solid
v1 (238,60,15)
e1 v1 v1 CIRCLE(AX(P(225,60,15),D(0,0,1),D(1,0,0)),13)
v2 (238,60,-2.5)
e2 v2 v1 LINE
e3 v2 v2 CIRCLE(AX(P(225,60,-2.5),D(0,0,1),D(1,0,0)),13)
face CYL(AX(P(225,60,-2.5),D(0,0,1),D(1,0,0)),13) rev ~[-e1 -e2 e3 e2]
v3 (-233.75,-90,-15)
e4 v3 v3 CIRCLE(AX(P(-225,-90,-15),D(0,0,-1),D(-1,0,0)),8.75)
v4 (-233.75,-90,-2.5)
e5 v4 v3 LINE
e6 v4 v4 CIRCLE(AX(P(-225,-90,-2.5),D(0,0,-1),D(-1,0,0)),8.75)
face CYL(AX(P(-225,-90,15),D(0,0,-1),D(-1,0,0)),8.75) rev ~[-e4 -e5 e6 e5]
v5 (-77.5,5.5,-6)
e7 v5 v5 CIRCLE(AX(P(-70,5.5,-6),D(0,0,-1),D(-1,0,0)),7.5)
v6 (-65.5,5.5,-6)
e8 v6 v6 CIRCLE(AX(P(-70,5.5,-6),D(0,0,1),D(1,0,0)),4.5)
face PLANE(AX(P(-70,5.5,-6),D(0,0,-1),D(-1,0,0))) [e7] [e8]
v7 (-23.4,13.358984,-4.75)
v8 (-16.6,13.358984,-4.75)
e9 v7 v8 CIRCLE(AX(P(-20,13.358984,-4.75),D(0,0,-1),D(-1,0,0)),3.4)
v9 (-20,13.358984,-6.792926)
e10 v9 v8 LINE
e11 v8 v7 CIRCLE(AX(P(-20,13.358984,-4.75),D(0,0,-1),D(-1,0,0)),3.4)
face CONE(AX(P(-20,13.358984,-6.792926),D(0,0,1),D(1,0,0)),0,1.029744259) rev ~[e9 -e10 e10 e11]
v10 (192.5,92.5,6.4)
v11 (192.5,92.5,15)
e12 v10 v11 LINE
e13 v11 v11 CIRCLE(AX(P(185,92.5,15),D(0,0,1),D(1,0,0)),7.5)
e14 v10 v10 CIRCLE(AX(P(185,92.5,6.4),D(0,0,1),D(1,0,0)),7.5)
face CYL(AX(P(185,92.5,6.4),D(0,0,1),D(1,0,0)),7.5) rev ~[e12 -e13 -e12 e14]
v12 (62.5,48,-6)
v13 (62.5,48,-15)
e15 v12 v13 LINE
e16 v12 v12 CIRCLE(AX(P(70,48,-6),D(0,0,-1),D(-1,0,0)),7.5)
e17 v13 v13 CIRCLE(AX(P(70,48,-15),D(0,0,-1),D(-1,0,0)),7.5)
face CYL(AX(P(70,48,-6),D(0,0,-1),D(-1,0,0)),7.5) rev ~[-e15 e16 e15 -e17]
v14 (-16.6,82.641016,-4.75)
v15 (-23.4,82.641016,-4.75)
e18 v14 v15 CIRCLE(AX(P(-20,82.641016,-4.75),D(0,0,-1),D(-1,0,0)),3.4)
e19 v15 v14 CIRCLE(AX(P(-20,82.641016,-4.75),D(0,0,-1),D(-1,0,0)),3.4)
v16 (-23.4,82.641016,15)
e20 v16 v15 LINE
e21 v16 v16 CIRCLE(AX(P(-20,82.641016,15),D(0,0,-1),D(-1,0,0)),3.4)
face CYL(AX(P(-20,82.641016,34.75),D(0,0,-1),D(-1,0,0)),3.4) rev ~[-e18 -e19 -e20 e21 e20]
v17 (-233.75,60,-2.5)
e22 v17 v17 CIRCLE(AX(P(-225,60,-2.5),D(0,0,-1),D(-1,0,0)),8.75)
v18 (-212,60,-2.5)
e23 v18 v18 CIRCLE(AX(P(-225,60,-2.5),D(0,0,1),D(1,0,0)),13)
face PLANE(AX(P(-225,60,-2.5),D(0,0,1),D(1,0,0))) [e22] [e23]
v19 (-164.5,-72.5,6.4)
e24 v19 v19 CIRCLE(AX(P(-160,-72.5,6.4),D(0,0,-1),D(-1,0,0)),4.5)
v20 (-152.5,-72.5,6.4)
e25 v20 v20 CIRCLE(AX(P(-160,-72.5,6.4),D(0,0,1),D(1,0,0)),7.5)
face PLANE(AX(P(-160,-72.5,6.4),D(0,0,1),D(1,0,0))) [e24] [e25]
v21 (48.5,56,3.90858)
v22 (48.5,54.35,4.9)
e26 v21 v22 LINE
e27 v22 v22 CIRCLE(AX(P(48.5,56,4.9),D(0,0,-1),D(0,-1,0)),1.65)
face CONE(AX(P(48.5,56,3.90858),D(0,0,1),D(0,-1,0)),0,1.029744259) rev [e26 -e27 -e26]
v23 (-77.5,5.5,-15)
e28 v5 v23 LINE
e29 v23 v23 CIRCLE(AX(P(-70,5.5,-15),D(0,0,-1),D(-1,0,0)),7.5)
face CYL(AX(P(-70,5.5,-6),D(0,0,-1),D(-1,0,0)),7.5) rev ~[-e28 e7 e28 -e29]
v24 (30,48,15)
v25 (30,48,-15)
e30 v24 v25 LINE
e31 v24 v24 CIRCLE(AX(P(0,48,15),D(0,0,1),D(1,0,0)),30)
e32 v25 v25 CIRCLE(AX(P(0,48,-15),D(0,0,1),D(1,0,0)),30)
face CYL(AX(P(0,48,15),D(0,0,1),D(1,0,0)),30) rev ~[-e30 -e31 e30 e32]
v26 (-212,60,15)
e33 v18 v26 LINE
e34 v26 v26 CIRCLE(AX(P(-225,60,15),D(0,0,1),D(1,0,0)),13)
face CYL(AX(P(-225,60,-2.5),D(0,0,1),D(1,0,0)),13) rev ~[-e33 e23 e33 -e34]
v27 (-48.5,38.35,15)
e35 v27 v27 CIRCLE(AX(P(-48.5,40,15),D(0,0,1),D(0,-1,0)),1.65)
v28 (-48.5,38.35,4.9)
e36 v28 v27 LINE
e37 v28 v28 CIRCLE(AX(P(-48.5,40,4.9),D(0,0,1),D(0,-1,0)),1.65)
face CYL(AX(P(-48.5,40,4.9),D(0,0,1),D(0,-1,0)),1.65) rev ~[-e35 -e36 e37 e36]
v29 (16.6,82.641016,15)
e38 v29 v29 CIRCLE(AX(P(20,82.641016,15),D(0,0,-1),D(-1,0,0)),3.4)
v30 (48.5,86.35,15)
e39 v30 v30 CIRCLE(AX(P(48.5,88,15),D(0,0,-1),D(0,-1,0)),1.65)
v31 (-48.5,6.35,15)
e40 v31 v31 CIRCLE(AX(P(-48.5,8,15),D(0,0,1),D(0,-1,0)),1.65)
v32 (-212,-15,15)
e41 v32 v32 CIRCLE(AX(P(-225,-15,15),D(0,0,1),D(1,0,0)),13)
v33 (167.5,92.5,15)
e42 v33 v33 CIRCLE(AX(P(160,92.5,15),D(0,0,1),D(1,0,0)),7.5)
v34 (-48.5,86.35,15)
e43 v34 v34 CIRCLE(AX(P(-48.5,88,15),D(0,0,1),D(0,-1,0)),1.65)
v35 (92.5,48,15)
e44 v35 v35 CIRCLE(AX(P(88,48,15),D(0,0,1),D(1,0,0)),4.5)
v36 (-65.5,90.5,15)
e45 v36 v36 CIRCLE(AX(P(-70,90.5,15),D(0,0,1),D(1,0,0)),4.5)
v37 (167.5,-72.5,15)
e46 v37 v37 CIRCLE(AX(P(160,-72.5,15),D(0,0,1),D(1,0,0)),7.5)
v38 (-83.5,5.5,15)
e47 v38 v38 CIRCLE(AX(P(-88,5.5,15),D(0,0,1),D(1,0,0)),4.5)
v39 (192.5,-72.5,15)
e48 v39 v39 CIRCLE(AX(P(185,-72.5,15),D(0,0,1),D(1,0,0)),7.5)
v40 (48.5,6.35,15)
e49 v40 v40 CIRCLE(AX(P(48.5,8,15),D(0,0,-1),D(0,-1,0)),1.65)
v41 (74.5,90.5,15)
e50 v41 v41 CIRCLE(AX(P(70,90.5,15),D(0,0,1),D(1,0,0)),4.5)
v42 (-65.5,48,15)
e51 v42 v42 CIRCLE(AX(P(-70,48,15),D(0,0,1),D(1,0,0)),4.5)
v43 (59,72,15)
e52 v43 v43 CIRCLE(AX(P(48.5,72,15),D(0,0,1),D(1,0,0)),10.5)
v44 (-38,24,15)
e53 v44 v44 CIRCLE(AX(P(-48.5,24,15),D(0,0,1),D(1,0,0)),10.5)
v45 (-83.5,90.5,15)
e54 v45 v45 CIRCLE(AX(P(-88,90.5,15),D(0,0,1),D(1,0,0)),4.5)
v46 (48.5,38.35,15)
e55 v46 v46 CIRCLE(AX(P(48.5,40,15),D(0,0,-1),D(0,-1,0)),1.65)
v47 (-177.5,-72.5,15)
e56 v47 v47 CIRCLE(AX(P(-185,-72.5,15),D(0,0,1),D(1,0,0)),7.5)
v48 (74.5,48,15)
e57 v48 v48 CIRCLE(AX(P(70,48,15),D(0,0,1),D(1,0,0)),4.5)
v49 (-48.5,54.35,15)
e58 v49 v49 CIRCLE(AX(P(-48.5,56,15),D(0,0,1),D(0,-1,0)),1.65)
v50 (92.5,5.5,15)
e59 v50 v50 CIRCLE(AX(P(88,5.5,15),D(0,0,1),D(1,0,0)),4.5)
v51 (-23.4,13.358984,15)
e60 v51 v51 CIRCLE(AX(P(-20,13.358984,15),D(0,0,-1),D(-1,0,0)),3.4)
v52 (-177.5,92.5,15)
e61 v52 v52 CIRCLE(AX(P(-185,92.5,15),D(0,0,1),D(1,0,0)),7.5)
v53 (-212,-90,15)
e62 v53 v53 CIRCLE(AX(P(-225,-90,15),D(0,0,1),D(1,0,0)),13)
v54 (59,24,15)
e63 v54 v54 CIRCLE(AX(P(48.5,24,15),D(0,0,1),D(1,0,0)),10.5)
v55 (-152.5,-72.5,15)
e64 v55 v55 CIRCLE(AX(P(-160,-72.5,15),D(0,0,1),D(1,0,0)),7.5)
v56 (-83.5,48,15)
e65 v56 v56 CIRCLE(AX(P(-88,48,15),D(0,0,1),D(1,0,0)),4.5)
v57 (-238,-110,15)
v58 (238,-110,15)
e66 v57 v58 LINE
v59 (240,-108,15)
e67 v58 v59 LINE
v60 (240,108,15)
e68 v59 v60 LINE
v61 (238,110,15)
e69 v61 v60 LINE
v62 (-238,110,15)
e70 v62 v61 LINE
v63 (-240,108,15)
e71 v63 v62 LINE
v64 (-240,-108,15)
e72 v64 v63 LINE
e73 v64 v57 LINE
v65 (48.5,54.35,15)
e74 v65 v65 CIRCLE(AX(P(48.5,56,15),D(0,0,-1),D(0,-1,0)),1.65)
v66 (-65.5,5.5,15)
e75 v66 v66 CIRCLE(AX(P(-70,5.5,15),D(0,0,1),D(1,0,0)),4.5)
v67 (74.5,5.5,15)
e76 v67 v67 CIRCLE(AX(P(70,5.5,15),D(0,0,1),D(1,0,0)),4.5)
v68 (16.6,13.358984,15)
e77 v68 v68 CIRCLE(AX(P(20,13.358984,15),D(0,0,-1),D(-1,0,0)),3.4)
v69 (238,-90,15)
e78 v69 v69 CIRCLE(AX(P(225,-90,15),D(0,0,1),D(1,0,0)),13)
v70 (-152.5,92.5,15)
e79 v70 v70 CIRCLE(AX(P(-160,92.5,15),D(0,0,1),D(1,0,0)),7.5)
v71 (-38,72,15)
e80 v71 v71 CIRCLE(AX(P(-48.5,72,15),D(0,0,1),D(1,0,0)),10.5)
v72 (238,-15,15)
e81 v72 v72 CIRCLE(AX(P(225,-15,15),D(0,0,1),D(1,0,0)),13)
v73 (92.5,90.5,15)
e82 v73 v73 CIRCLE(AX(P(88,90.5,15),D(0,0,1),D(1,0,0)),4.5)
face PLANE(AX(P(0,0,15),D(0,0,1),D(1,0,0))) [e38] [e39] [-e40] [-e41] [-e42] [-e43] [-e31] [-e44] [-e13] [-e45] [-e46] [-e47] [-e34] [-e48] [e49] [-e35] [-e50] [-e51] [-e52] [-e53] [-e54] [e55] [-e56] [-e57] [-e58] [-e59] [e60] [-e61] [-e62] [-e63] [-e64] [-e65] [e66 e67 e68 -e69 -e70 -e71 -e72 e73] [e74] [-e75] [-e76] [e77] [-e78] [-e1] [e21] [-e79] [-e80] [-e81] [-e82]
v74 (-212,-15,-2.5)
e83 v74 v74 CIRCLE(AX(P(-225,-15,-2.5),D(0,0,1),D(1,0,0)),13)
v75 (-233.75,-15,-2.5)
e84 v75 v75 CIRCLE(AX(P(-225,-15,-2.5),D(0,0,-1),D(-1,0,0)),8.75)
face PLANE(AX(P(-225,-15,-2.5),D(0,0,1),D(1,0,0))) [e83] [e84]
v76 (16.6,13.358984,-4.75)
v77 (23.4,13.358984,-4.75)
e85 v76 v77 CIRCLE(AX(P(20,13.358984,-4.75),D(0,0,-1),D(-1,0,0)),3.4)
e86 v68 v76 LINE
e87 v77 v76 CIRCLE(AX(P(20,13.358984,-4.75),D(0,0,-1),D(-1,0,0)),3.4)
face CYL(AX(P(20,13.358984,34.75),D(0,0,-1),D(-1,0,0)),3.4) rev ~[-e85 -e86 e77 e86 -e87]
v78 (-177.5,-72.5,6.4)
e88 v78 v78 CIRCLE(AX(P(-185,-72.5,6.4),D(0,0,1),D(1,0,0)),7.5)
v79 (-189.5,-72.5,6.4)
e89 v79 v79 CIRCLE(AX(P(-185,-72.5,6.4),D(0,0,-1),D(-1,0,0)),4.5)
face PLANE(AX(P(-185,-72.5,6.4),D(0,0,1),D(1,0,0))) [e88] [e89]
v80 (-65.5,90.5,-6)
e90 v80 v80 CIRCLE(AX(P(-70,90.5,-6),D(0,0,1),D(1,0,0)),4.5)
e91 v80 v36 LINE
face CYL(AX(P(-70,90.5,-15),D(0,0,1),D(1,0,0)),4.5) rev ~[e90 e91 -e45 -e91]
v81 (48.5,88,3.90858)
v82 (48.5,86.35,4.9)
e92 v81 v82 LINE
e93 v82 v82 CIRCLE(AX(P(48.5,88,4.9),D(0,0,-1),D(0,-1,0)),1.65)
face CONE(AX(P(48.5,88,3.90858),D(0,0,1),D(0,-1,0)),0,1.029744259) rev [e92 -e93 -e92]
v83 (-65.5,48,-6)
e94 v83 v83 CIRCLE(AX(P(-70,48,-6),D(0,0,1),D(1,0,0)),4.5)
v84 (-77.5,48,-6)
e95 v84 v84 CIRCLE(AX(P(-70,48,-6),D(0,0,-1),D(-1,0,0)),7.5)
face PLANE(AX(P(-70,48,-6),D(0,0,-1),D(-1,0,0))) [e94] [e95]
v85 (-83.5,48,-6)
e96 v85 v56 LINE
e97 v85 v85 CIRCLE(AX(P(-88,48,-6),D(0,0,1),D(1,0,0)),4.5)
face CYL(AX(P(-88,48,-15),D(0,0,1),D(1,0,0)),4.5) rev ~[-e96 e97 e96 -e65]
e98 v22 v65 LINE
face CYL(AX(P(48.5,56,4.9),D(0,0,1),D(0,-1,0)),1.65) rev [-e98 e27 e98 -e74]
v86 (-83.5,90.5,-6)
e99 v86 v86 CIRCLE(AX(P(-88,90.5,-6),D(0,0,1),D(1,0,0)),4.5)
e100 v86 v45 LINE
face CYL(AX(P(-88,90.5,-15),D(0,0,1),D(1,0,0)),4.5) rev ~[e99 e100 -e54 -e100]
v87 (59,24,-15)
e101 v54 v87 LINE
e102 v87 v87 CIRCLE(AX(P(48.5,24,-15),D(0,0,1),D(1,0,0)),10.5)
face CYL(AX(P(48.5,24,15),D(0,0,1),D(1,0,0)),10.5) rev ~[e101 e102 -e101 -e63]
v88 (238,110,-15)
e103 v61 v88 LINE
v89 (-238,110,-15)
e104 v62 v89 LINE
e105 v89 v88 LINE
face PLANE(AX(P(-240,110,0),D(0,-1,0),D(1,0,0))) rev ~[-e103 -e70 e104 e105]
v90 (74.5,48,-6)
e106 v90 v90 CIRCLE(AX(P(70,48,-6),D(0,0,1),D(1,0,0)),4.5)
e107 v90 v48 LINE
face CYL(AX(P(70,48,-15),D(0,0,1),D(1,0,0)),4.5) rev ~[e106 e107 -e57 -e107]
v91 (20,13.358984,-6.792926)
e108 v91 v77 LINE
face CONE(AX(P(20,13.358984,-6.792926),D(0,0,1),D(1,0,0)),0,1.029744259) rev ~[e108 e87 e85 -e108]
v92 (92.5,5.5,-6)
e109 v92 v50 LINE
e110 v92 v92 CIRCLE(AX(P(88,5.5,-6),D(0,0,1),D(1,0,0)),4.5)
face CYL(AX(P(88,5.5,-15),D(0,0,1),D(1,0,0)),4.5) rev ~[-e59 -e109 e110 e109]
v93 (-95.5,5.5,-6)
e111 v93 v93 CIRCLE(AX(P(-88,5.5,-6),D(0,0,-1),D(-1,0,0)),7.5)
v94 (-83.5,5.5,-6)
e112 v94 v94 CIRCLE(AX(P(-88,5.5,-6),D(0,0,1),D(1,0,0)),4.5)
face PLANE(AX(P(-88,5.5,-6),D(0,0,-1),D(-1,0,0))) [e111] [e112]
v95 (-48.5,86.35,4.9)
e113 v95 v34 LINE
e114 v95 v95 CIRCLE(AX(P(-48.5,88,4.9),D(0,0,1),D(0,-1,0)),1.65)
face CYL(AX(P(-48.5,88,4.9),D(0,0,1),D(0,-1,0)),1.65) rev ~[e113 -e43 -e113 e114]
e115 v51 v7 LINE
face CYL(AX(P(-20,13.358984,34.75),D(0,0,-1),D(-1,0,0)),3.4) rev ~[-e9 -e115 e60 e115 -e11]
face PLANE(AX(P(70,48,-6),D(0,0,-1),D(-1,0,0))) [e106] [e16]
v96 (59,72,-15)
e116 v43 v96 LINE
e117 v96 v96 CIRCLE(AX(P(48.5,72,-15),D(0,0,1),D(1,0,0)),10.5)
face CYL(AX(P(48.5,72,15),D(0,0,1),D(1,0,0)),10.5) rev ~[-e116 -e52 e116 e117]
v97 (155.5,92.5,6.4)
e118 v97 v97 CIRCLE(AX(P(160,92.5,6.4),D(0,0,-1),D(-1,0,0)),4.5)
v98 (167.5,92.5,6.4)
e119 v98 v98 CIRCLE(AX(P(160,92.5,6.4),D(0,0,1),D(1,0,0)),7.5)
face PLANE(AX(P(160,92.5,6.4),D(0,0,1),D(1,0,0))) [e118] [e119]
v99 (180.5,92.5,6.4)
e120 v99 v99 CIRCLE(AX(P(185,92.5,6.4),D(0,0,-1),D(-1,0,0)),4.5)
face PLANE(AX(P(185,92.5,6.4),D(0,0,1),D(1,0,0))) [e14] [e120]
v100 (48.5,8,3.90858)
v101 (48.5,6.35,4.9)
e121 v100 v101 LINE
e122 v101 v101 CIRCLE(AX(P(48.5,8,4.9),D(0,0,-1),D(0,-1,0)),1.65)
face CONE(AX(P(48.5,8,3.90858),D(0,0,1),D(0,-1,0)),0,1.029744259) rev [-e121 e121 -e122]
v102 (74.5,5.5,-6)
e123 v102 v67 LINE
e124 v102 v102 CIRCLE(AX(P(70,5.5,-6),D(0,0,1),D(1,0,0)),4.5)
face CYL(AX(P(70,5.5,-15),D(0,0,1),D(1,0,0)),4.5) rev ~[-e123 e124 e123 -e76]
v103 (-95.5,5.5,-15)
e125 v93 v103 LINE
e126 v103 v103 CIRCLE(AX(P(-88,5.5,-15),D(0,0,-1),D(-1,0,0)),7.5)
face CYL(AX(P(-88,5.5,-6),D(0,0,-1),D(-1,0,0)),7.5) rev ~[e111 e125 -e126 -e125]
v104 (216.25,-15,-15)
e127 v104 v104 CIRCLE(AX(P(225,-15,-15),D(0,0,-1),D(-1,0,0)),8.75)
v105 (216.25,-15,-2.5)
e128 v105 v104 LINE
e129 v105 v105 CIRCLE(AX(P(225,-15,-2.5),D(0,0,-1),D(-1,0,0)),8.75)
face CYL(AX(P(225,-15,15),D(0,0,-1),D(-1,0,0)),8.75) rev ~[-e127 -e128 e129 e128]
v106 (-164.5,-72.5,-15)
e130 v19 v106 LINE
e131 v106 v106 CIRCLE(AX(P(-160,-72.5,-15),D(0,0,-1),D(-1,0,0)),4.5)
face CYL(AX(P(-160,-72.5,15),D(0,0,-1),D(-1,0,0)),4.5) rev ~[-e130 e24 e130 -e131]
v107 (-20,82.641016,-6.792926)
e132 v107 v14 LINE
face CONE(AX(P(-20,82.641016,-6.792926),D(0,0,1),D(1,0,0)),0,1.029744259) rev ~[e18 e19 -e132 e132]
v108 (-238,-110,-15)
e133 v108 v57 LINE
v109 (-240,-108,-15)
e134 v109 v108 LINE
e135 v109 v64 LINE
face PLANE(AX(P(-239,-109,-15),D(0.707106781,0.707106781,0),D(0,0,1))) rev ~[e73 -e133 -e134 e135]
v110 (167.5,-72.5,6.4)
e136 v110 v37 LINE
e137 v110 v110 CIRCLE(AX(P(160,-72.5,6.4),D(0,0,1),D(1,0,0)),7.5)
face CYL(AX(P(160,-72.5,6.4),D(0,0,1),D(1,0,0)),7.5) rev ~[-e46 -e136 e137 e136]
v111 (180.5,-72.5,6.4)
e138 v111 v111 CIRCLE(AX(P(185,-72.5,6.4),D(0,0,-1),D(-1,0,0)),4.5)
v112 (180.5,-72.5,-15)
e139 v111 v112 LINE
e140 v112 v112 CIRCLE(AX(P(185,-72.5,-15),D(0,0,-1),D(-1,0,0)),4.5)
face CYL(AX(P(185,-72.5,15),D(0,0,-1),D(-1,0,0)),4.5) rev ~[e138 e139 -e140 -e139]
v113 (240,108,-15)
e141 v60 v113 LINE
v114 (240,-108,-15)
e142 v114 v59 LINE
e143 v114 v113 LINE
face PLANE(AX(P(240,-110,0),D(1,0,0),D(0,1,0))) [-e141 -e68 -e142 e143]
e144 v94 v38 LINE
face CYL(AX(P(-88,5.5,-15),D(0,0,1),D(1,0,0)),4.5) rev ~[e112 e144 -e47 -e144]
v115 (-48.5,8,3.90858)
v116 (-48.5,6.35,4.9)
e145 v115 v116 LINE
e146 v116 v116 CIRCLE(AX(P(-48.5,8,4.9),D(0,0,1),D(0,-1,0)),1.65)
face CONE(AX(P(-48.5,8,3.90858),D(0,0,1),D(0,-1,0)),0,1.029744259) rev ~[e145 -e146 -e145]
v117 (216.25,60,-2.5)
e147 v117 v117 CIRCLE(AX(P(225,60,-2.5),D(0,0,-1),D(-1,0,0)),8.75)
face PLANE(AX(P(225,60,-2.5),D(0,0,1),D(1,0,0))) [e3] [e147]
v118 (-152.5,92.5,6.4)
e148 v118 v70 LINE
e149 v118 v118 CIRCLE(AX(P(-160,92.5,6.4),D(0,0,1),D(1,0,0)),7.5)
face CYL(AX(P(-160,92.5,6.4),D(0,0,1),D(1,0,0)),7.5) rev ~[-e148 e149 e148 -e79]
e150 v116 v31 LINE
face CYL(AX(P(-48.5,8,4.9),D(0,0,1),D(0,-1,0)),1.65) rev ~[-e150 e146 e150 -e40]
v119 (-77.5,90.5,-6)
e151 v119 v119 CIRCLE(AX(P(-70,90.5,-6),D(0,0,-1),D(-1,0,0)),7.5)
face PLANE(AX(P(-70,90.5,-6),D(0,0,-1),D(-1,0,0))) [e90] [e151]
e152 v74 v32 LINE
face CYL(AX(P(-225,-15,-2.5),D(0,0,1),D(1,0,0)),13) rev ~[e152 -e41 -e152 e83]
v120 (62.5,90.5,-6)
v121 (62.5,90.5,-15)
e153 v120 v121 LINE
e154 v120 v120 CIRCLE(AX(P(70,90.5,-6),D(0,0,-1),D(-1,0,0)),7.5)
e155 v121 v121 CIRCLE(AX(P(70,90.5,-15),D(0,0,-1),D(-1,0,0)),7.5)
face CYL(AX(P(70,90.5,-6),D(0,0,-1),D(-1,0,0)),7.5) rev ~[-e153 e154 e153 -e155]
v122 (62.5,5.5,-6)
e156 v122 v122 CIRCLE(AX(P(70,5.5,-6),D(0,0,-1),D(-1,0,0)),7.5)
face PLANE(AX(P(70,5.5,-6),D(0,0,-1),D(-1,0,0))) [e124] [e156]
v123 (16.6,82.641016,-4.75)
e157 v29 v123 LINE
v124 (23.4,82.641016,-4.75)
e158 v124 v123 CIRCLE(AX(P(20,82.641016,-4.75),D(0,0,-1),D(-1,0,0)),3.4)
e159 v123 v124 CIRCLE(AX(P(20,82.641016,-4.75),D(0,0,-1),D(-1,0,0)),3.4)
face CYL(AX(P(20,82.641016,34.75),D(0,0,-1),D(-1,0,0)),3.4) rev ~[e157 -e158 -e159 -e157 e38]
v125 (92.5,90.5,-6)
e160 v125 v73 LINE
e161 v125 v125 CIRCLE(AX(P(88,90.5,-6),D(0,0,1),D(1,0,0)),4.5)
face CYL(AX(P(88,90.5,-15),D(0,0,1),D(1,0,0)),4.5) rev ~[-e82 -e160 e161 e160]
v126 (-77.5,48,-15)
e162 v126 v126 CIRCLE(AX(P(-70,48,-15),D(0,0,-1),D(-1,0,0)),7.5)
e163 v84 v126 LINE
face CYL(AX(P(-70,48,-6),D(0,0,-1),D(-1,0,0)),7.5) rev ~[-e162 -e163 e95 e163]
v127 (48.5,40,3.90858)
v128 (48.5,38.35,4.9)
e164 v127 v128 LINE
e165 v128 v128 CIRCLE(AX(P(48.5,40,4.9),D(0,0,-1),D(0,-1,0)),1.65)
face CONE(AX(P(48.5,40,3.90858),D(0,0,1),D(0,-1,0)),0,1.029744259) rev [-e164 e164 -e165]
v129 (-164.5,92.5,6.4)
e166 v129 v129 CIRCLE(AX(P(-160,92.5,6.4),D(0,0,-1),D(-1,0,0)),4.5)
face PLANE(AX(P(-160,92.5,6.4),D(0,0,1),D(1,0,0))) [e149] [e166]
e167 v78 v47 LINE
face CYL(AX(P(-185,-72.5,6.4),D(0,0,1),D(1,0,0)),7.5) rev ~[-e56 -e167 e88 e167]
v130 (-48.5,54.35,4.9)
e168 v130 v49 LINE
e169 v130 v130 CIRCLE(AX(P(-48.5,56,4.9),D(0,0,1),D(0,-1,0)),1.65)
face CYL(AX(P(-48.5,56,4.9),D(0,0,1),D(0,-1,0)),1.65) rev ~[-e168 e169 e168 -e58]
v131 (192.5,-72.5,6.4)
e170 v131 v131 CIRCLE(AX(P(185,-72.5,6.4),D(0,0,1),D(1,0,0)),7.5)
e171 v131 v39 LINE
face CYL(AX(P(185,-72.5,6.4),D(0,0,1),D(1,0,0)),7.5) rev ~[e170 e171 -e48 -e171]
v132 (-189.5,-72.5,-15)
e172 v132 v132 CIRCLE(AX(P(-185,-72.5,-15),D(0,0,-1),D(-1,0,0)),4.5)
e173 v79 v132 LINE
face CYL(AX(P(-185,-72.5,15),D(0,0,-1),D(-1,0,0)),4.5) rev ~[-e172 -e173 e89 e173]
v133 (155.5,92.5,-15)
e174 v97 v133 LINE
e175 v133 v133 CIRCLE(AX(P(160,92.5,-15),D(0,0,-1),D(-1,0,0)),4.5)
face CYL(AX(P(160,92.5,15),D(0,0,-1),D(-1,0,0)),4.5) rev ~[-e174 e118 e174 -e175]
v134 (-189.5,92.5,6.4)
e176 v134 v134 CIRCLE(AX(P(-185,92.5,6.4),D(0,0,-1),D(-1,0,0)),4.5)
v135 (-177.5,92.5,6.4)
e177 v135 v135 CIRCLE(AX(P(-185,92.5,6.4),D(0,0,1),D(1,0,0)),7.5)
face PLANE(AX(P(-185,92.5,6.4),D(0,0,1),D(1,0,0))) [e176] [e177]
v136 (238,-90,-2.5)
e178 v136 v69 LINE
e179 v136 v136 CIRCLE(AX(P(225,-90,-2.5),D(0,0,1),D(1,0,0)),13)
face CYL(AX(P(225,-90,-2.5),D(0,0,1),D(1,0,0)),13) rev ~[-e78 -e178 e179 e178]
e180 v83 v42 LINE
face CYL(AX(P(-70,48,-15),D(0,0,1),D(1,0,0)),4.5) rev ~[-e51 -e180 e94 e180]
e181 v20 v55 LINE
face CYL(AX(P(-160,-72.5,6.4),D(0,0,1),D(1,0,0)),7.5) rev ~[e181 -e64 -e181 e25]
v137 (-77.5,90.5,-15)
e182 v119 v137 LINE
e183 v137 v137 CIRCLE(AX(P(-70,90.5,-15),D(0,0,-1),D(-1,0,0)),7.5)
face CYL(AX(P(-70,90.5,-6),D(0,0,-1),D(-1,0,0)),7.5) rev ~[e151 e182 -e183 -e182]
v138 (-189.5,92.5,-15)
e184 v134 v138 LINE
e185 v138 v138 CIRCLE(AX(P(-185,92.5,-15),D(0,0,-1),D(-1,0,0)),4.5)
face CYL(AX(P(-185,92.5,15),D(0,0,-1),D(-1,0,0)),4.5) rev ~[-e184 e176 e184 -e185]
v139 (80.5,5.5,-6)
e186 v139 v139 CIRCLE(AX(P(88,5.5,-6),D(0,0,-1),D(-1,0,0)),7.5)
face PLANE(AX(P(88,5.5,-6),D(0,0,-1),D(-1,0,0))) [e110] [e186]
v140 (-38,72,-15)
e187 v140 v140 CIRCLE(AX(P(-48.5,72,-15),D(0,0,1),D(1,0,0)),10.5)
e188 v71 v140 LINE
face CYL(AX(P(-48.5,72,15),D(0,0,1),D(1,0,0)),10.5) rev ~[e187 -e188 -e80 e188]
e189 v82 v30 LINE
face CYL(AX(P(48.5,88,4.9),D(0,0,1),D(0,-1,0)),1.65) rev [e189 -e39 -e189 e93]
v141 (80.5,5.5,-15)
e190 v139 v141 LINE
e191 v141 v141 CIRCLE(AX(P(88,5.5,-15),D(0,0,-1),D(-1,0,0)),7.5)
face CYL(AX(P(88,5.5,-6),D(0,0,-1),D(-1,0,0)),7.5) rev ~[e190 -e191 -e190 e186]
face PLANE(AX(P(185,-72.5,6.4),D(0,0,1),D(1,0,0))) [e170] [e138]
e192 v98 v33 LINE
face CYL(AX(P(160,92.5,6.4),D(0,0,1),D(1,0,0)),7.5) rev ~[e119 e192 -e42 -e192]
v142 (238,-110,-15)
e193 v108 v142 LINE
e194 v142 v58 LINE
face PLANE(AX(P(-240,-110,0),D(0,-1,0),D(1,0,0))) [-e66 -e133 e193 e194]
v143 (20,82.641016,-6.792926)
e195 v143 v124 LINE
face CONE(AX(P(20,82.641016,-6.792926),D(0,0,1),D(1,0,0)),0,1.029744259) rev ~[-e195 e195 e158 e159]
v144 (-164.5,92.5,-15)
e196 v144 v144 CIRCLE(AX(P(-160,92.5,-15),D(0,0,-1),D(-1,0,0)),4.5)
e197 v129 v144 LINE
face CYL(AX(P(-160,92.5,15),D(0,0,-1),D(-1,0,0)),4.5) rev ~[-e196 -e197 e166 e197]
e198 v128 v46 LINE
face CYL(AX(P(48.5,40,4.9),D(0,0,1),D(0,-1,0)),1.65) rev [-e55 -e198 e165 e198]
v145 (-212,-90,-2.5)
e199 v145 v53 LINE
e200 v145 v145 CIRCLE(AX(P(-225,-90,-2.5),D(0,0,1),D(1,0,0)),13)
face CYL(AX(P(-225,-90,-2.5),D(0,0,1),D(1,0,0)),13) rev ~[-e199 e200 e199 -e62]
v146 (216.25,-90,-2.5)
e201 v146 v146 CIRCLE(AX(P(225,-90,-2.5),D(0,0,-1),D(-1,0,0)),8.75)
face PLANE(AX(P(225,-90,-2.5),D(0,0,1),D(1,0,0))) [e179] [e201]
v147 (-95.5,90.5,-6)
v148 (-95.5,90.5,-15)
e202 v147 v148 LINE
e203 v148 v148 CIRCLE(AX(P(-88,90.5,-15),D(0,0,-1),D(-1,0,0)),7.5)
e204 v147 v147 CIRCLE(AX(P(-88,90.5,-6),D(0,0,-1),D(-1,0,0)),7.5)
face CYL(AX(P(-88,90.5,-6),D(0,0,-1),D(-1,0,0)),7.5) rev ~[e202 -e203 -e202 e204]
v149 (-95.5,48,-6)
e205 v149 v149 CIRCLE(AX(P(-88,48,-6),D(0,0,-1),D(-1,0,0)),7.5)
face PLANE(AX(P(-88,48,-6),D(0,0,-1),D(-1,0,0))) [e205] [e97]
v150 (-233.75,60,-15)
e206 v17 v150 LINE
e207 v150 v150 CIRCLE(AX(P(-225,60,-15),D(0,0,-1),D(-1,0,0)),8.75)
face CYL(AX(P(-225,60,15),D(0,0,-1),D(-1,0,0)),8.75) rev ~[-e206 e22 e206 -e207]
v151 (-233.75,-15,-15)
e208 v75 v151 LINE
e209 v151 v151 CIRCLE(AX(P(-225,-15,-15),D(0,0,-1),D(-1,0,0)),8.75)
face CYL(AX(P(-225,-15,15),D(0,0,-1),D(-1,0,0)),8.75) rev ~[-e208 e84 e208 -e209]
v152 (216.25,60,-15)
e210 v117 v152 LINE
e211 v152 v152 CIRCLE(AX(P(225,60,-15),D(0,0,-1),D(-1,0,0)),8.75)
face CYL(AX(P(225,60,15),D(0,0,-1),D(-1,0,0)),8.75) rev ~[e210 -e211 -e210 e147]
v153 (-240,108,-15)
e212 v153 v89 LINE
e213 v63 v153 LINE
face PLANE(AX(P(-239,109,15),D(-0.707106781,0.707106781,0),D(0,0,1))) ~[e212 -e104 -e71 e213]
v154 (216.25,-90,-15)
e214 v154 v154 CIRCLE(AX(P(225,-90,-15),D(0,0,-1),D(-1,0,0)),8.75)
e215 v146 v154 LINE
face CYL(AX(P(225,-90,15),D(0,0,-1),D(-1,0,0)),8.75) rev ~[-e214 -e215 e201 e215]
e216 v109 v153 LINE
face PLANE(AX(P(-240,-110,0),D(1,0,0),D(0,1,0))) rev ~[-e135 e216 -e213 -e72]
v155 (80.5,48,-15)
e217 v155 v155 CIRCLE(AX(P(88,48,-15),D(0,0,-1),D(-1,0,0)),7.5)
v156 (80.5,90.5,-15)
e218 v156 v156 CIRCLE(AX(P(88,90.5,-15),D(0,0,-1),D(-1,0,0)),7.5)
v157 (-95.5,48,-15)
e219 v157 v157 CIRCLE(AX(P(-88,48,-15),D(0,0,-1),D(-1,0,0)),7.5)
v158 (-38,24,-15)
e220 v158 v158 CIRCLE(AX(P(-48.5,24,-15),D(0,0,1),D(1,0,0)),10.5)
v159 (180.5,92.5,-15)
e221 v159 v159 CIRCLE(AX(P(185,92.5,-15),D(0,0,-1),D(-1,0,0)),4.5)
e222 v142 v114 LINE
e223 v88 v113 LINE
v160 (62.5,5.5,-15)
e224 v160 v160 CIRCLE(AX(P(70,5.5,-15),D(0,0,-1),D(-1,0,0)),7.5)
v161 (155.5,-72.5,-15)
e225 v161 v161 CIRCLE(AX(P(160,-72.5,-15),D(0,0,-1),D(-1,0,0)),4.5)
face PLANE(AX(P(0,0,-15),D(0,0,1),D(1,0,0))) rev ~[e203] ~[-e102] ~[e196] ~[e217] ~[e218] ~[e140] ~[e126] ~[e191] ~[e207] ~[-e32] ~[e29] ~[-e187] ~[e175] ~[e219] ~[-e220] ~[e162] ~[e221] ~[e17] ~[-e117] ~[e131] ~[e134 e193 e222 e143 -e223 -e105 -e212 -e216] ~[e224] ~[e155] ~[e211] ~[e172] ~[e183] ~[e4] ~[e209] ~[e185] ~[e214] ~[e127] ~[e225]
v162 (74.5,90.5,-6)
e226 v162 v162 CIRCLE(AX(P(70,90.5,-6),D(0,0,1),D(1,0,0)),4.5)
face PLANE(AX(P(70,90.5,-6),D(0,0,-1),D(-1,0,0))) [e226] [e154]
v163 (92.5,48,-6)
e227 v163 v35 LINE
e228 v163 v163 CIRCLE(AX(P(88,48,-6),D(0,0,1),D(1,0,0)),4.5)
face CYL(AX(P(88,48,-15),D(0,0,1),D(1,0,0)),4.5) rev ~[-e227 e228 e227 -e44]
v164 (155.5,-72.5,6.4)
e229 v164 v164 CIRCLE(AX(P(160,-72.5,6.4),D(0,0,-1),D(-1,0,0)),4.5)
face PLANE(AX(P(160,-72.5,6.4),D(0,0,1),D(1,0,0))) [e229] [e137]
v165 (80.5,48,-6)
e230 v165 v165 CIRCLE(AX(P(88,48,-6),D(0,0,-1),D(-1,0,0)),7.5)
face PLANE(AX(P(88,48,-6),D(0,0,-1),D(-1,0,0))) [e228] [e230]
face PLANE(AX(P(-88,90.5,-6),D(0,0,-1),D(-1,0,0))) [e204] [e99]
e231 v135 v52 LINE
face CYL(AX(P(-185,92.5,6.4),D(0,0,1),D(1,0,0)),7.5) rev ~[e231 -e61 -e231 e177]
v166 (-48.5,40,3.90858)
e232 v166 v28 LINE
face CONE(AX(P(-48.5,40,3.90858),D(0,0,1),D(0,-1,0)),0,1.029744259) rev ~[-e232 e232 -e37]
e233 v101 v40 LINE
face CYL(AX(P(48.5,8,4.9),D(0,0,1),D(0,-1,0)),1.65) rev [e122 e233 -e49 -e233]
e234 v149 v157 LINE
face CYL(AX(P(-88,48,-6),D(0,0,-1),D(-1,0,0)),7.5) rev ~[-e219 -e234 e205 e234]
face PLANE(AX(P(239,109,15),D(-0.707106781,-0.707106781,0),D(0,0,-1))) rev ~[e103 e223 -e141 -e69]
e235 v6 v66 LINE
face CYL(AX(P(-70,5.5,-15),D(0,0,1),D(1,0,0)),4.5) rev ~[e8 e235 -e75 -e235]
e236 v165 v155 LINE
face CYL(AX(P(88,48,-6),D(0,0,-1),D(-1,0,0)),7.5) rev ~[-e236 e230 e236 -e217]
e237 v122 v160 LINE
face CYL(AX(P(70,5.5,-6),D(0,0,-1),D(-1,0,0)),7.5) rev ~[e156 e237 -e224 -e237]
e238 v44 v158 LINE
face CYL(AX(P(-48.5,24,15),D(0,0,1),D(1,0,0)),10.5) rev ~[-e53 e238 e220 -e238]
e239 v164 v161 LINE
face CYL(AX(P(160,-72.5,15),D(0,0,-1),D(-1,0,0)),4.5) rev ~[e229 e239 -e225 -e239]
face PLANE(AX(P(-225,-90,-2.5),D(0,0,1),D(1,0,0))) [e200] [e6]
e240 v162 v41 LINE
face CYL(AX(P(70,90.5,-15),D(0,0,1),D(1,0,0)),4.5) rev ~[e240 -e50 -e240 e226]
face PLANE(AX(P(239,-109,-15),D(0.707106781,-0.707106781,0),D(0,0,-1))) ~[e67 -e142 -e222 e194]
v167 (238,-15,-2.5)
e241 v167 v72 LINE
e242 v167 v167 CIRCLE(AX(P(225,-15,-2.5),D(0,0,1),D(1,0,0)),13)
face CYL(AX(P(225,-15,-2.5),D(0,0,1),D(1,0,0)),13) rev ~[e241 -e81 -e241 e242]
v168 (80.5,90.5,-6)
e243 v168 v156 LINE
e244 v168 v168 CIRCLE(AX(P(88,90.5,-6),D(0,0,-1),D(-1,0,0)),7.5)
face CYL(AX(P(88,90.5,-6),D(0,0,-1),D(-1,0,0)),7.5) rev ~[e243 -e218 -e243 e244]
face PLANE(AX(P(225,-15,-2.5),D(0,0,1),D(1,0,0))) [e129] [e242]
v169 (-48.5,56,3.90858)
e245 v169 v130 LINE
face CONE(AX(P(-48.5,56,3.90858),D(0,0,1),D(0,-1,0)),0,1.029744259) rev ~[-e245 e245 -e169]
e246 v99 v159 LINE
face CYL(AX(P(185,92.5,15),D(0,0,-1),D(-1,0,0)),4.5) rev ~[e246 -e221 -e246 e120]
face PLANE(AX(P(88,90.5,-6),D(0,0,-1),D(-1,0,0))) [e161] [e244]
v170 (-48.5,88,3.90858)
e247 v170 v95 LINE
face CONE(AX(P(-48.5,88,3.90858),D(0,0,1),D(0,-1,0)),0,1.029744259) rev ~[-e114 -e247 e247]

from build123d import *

# Parameters (mm, degrees)
SKETCH1_W                                            = 480
SKETCH1_H                                            = 220
BOSS_EXTRUDE1_DEPTH                                  = 15
HOLE_SIZE_PER_SOCKET_HEAD_CAP_SCREW_TYPE_D           = 17.5
HOLE_SIZE_PER_SOCKET_HEAD_CAP_SCREW_TYPE_CBORE_D     = 26
HOLE_SIZE_PER_SOCKET_HEAD_CAP_SCREW_TYPE_CBORE_DEPTH = 17.5
CHAMFER1_SIZE                                        = 2
SKETCH4_R                                            = 30
CUT_EXTRUDE1_DEPTH                                   = 266.706605112
M8_TAPPED_HOLE1_D                                    = 6.8
M8_TAPPED_HOLE1_DEPTH                                = 19.75
M8_TAPPED_HOLE1_TIP                                  = 2.042926105
HOLE_WIZARD_2_D                                      = 9
HOLE_WIZARD_2_CBORE_D                                = 15
HOLE_WIZARD_2_CBORE_DEPTH                            = 9
SKETCH9_R                                            = 10.5
CUT_EXTRUDE2_DEPTH                                   = 266.706605112
M4_TAPPED_HOLE1_AT_2_COUNT                           = 2
M4_TAPPED_HOLE1_AT_2_PITCH                           = 32
M4_TAPPED_HOLE1_AT_3_COUNT                           = 2
M4_TAPPED_HOLE1_AT_3_PITCH                           = 48
M4_TAPPED_HOLE1_AT_4_COUNT                           = 2
M4_TAPPED_HOLE1_AT_4_PITCH                           = 80
CBORE_FOR_M8_HEX_SOCKET_HEAD_CAP_SCREW1_D            = 9
CBORE_FOR_M8_HEX_SOCKET_HEAD_CAP_SCREW1_CBORE_D      = 15
CBORE_FOR_M8_HEX_SOCKET_HEAD_CAP_SCREW1_CBORE_DEPTH  = 8.6


with BuildPart() as part:
    # Sketch1 → Boss-Extrude1 (new, symmetric)
    with BuildSketch(Plane.XY):
        Rectangle(SKETCH1_W, SKETCH1_H)
    extrude(amount=BOSS_EXTRUDE1_DEPTH, both=True)

    # Hole size per socket head cap screw type2 (through all)
    with Locations(Plane.XY.offset(15)):
        with Locations((-225, 60), (225, 60), (225, -90), (-225, -90), (-225, -15), (225, -15)):
            CounterBoreHole(HOLE_SIZE_PER_SOCKET_HEAD_CAP_SCREW_TYPE_D / 2, HOLE_SIZE_PER_SOCKET_HEAD_CAP_SCREW_TYPE_CBORE_D / 2, HOLE_SIZE_PER_SOCKET_HEAD_CAP_SCREW_TYPE_CBORE_DEPTH)

    # Chamfer1
    chamfer1_edges = [part.edges().sort_by_distance(p)[0] for p in [
        (240, -110, 0),
        (-240, -110, 0),
        (-240, 110, 0),
        (240, 110, 0),
    ]]
    chamfer(chamfer1_edges, length=CHAMFER1_SIZE)

    # Sketch4 → Cut-Extrude1 (cut, through all)
    with BuildSketch(Plane.XY.offset(15)):
        with Locations((0, 48)):
            Circle(SKETCH4_R)
    extrude(amount=-CUT_EXTRUDE1_DEPTH, mode=Mode.SUBTRACT)

    # M8 Tapped Hole1
    with Locations(Plane.XY.offset(15)):
        with Locations((-20, 82.641016151), (20, 82.641016151), (-20, 13.358983849), (20, 13.358983849)):
            Hole(M8_TAPPED_HOLE1_D / 2, depth=M8_TAPPED_HOLE1_DEPTH)
            with Locations((0, 0, -(M8_TAPPED_HOLE1_DEPTH + M8_TAPPED_HOLE1_TIP / 2))):  # 118° drill point
                Cone(0, M8_TAPPED_HOLE1_D / 2, M8_TAPPED_HOLE1_TIP, mode=Mode.SUBTRACT)

    # 打孔尺寸根据内六角圆柱头螺钉的类型2 (through all)
    with Locations(Plane(origin=(0, 0, -15), x_dir=(-1, 0, 0), z_dir=(0, 0, -1))):
        with Locations((-88, 90.5), (-70, 90.5), (-70, 48), (-88, 48), (-88, 5.5), (-70, 5.5), (70, 90.5), (88, 90.5), (70, 48), (88, 48), (70, 5.5), (88, 5.5)):
            CounterBoreHole(HOLE_WIZARD_2_D / 2, HOLE_WIZARD_2_CBORE_D / 2, HOLE_WIZARD_2_CBORE_DEPTH)

    # Sketch9 → Cut-Extrude2 (cut, through all)
    with BuildSketch(Plane.XY.offset(15)):
        with Locations((-48.5, 72)):
            Circle(SKETCH9_R)
        with Locations((-48.5, 24)):
            Circle(SKETCH9_R)
        with Locations((48.5, 24)):
            Circle(SKETCH9_R)
        with Locations((48.5, 72)):
            Circle(SKETCH9_R)
    extrude(amount=-CUT_EXTRUDE2_DEPTH, mode=Mode.SUBTRACT)

    # Sketch10 → M4 Tapped Hole1 (revolve, cut)
    with BuildSketch(Plane(origin=(48.5, 88, 15), x_dir=(0, -1, 0), z_dir=(1, 0, 0))):
        Polygon((0, 0), (0, 11.091420021), (1.65, 10.1), (1.65, 0), align=None)
    m4_tapped_hole1 = revolve(axis=Axis((48.5, 88, 21.35), (0, 0, -1)), mode=Mode.SUBTRACT)

    # M4 Tapped Hole1 at 2: M4 Tapped Hole1 ×2
    with Locations(*[(0, -i * M4_TAPPED_HOLE1_AT_2_PITCH, 0) for i in range(1, M4_TAPPED_HOLE1_AT_2_COUNT)]):
        add(m4_tapped_hole1, mode=Mode.SUBTRACT)

    # M4 Tapped Hole1 at 3: M4 Tapped Hole1 ×2
    with Locations(*[(0, -i * M4_TAPPED_HOLE1_AT_3_PITCH, 0) for i in range(1, M4_TAPPED_HOLE1_AT_3_COUNT)]):
        add(m4_tapped_hole1, mode=Mode.SUBTRACT)

    # M4 Tapped Hole1 at 4: M4 Tapped Hole1 ×2
    with Locations(*[(0, -i * M4_TAPPED_HOLE1_AT_4_PITCH, 0) for i in range(1, M4_TAPPED_HOLE1_AT_4_COUNT)]):
        add(m4_tapped_hole1, mode=Mode.SUBTRACT)

    # Mirror1: M4 Tapped Hole1 across plane
    add(m4_tapped_hole1.mirror(Plane(origin=(0, 0, 0), x_dir=(0, 0, 1), z_dir=(1, 0, 0))), mode=Mode.SUBTRACT)

    # Mirror1 copy 1 sketch → Mirror1 copy 1 (revolve, cut)
    with BuildSketch(Plane(origin=(-48.5, 56, 15), x_dir=(0, -1, 0), z_dir=(-1, 0, 0))):
        Polygon((0, 0), (0, -11.091420021), (1.65, -10.1), (1.65, 0), align=None)
    revolve(axis=Axis((-48.5, 56, 21.35), (0, 0, 1)), mode=Mode.SUBTRACT)

    # Mirror1 copy 2 sketch → Mirror1 copy 2 (revolve, cut)
    with BuildSketch(Plane(origin=(-48.5, 40, 15), x_dir=(0, -1, 0), z_dir=(-1, 0, 0))):
        Polygon((0, 0), (0, -11.091420021), (1.65, -10.1), (1.65, 0), align=None)
    revolve(axis=Axis((-48.5, 40, 21.35), (0, 0, 1)), mode=Mode.SUBTRACT)

    # Mirror1 copy 3 sketch → Mirror1 copy 3 (revolve, cut)
    with BuildSketch(Plane(origin=(-48.5, 8, 15), x_dir=(0, -1, 0), z_dir=(-1, 0, 0))):
        Polygon((0, 0), (0, -11.091420021), (1.65, -10.1), (1.65, 0), align=None)
    revolve(axis=Axis((-48.5, 8, 21.35), (0, 0, 1)), mode=Mode.SUBTRACT)

    # CBORE for M8 Hex Socket Head Cap Screw1 (through all)
    with Locations(Plane.XY.offset(15)):
        with Locations((-185, -72.5), (-160, -72.5), (-185, 92.5), (-160, 92.5), (185, 92.5), (160, 92.5), (185, -72.5), (160, -72.5)):
            CounterBoreHole(CBORE_FOR_M8_HEX_SOCKET_HEAD_CAP_SCREW1_D / 2, CBORE_FOR_M8_HEX_SOCKET_HEAD_CAP_SCREW1_CBORE_D / 2, CBORE_FOR_M8_HEX_SOCKET_HEAD_CAP_SCREW1_CBORE_DEPTH)


solid = part.part
